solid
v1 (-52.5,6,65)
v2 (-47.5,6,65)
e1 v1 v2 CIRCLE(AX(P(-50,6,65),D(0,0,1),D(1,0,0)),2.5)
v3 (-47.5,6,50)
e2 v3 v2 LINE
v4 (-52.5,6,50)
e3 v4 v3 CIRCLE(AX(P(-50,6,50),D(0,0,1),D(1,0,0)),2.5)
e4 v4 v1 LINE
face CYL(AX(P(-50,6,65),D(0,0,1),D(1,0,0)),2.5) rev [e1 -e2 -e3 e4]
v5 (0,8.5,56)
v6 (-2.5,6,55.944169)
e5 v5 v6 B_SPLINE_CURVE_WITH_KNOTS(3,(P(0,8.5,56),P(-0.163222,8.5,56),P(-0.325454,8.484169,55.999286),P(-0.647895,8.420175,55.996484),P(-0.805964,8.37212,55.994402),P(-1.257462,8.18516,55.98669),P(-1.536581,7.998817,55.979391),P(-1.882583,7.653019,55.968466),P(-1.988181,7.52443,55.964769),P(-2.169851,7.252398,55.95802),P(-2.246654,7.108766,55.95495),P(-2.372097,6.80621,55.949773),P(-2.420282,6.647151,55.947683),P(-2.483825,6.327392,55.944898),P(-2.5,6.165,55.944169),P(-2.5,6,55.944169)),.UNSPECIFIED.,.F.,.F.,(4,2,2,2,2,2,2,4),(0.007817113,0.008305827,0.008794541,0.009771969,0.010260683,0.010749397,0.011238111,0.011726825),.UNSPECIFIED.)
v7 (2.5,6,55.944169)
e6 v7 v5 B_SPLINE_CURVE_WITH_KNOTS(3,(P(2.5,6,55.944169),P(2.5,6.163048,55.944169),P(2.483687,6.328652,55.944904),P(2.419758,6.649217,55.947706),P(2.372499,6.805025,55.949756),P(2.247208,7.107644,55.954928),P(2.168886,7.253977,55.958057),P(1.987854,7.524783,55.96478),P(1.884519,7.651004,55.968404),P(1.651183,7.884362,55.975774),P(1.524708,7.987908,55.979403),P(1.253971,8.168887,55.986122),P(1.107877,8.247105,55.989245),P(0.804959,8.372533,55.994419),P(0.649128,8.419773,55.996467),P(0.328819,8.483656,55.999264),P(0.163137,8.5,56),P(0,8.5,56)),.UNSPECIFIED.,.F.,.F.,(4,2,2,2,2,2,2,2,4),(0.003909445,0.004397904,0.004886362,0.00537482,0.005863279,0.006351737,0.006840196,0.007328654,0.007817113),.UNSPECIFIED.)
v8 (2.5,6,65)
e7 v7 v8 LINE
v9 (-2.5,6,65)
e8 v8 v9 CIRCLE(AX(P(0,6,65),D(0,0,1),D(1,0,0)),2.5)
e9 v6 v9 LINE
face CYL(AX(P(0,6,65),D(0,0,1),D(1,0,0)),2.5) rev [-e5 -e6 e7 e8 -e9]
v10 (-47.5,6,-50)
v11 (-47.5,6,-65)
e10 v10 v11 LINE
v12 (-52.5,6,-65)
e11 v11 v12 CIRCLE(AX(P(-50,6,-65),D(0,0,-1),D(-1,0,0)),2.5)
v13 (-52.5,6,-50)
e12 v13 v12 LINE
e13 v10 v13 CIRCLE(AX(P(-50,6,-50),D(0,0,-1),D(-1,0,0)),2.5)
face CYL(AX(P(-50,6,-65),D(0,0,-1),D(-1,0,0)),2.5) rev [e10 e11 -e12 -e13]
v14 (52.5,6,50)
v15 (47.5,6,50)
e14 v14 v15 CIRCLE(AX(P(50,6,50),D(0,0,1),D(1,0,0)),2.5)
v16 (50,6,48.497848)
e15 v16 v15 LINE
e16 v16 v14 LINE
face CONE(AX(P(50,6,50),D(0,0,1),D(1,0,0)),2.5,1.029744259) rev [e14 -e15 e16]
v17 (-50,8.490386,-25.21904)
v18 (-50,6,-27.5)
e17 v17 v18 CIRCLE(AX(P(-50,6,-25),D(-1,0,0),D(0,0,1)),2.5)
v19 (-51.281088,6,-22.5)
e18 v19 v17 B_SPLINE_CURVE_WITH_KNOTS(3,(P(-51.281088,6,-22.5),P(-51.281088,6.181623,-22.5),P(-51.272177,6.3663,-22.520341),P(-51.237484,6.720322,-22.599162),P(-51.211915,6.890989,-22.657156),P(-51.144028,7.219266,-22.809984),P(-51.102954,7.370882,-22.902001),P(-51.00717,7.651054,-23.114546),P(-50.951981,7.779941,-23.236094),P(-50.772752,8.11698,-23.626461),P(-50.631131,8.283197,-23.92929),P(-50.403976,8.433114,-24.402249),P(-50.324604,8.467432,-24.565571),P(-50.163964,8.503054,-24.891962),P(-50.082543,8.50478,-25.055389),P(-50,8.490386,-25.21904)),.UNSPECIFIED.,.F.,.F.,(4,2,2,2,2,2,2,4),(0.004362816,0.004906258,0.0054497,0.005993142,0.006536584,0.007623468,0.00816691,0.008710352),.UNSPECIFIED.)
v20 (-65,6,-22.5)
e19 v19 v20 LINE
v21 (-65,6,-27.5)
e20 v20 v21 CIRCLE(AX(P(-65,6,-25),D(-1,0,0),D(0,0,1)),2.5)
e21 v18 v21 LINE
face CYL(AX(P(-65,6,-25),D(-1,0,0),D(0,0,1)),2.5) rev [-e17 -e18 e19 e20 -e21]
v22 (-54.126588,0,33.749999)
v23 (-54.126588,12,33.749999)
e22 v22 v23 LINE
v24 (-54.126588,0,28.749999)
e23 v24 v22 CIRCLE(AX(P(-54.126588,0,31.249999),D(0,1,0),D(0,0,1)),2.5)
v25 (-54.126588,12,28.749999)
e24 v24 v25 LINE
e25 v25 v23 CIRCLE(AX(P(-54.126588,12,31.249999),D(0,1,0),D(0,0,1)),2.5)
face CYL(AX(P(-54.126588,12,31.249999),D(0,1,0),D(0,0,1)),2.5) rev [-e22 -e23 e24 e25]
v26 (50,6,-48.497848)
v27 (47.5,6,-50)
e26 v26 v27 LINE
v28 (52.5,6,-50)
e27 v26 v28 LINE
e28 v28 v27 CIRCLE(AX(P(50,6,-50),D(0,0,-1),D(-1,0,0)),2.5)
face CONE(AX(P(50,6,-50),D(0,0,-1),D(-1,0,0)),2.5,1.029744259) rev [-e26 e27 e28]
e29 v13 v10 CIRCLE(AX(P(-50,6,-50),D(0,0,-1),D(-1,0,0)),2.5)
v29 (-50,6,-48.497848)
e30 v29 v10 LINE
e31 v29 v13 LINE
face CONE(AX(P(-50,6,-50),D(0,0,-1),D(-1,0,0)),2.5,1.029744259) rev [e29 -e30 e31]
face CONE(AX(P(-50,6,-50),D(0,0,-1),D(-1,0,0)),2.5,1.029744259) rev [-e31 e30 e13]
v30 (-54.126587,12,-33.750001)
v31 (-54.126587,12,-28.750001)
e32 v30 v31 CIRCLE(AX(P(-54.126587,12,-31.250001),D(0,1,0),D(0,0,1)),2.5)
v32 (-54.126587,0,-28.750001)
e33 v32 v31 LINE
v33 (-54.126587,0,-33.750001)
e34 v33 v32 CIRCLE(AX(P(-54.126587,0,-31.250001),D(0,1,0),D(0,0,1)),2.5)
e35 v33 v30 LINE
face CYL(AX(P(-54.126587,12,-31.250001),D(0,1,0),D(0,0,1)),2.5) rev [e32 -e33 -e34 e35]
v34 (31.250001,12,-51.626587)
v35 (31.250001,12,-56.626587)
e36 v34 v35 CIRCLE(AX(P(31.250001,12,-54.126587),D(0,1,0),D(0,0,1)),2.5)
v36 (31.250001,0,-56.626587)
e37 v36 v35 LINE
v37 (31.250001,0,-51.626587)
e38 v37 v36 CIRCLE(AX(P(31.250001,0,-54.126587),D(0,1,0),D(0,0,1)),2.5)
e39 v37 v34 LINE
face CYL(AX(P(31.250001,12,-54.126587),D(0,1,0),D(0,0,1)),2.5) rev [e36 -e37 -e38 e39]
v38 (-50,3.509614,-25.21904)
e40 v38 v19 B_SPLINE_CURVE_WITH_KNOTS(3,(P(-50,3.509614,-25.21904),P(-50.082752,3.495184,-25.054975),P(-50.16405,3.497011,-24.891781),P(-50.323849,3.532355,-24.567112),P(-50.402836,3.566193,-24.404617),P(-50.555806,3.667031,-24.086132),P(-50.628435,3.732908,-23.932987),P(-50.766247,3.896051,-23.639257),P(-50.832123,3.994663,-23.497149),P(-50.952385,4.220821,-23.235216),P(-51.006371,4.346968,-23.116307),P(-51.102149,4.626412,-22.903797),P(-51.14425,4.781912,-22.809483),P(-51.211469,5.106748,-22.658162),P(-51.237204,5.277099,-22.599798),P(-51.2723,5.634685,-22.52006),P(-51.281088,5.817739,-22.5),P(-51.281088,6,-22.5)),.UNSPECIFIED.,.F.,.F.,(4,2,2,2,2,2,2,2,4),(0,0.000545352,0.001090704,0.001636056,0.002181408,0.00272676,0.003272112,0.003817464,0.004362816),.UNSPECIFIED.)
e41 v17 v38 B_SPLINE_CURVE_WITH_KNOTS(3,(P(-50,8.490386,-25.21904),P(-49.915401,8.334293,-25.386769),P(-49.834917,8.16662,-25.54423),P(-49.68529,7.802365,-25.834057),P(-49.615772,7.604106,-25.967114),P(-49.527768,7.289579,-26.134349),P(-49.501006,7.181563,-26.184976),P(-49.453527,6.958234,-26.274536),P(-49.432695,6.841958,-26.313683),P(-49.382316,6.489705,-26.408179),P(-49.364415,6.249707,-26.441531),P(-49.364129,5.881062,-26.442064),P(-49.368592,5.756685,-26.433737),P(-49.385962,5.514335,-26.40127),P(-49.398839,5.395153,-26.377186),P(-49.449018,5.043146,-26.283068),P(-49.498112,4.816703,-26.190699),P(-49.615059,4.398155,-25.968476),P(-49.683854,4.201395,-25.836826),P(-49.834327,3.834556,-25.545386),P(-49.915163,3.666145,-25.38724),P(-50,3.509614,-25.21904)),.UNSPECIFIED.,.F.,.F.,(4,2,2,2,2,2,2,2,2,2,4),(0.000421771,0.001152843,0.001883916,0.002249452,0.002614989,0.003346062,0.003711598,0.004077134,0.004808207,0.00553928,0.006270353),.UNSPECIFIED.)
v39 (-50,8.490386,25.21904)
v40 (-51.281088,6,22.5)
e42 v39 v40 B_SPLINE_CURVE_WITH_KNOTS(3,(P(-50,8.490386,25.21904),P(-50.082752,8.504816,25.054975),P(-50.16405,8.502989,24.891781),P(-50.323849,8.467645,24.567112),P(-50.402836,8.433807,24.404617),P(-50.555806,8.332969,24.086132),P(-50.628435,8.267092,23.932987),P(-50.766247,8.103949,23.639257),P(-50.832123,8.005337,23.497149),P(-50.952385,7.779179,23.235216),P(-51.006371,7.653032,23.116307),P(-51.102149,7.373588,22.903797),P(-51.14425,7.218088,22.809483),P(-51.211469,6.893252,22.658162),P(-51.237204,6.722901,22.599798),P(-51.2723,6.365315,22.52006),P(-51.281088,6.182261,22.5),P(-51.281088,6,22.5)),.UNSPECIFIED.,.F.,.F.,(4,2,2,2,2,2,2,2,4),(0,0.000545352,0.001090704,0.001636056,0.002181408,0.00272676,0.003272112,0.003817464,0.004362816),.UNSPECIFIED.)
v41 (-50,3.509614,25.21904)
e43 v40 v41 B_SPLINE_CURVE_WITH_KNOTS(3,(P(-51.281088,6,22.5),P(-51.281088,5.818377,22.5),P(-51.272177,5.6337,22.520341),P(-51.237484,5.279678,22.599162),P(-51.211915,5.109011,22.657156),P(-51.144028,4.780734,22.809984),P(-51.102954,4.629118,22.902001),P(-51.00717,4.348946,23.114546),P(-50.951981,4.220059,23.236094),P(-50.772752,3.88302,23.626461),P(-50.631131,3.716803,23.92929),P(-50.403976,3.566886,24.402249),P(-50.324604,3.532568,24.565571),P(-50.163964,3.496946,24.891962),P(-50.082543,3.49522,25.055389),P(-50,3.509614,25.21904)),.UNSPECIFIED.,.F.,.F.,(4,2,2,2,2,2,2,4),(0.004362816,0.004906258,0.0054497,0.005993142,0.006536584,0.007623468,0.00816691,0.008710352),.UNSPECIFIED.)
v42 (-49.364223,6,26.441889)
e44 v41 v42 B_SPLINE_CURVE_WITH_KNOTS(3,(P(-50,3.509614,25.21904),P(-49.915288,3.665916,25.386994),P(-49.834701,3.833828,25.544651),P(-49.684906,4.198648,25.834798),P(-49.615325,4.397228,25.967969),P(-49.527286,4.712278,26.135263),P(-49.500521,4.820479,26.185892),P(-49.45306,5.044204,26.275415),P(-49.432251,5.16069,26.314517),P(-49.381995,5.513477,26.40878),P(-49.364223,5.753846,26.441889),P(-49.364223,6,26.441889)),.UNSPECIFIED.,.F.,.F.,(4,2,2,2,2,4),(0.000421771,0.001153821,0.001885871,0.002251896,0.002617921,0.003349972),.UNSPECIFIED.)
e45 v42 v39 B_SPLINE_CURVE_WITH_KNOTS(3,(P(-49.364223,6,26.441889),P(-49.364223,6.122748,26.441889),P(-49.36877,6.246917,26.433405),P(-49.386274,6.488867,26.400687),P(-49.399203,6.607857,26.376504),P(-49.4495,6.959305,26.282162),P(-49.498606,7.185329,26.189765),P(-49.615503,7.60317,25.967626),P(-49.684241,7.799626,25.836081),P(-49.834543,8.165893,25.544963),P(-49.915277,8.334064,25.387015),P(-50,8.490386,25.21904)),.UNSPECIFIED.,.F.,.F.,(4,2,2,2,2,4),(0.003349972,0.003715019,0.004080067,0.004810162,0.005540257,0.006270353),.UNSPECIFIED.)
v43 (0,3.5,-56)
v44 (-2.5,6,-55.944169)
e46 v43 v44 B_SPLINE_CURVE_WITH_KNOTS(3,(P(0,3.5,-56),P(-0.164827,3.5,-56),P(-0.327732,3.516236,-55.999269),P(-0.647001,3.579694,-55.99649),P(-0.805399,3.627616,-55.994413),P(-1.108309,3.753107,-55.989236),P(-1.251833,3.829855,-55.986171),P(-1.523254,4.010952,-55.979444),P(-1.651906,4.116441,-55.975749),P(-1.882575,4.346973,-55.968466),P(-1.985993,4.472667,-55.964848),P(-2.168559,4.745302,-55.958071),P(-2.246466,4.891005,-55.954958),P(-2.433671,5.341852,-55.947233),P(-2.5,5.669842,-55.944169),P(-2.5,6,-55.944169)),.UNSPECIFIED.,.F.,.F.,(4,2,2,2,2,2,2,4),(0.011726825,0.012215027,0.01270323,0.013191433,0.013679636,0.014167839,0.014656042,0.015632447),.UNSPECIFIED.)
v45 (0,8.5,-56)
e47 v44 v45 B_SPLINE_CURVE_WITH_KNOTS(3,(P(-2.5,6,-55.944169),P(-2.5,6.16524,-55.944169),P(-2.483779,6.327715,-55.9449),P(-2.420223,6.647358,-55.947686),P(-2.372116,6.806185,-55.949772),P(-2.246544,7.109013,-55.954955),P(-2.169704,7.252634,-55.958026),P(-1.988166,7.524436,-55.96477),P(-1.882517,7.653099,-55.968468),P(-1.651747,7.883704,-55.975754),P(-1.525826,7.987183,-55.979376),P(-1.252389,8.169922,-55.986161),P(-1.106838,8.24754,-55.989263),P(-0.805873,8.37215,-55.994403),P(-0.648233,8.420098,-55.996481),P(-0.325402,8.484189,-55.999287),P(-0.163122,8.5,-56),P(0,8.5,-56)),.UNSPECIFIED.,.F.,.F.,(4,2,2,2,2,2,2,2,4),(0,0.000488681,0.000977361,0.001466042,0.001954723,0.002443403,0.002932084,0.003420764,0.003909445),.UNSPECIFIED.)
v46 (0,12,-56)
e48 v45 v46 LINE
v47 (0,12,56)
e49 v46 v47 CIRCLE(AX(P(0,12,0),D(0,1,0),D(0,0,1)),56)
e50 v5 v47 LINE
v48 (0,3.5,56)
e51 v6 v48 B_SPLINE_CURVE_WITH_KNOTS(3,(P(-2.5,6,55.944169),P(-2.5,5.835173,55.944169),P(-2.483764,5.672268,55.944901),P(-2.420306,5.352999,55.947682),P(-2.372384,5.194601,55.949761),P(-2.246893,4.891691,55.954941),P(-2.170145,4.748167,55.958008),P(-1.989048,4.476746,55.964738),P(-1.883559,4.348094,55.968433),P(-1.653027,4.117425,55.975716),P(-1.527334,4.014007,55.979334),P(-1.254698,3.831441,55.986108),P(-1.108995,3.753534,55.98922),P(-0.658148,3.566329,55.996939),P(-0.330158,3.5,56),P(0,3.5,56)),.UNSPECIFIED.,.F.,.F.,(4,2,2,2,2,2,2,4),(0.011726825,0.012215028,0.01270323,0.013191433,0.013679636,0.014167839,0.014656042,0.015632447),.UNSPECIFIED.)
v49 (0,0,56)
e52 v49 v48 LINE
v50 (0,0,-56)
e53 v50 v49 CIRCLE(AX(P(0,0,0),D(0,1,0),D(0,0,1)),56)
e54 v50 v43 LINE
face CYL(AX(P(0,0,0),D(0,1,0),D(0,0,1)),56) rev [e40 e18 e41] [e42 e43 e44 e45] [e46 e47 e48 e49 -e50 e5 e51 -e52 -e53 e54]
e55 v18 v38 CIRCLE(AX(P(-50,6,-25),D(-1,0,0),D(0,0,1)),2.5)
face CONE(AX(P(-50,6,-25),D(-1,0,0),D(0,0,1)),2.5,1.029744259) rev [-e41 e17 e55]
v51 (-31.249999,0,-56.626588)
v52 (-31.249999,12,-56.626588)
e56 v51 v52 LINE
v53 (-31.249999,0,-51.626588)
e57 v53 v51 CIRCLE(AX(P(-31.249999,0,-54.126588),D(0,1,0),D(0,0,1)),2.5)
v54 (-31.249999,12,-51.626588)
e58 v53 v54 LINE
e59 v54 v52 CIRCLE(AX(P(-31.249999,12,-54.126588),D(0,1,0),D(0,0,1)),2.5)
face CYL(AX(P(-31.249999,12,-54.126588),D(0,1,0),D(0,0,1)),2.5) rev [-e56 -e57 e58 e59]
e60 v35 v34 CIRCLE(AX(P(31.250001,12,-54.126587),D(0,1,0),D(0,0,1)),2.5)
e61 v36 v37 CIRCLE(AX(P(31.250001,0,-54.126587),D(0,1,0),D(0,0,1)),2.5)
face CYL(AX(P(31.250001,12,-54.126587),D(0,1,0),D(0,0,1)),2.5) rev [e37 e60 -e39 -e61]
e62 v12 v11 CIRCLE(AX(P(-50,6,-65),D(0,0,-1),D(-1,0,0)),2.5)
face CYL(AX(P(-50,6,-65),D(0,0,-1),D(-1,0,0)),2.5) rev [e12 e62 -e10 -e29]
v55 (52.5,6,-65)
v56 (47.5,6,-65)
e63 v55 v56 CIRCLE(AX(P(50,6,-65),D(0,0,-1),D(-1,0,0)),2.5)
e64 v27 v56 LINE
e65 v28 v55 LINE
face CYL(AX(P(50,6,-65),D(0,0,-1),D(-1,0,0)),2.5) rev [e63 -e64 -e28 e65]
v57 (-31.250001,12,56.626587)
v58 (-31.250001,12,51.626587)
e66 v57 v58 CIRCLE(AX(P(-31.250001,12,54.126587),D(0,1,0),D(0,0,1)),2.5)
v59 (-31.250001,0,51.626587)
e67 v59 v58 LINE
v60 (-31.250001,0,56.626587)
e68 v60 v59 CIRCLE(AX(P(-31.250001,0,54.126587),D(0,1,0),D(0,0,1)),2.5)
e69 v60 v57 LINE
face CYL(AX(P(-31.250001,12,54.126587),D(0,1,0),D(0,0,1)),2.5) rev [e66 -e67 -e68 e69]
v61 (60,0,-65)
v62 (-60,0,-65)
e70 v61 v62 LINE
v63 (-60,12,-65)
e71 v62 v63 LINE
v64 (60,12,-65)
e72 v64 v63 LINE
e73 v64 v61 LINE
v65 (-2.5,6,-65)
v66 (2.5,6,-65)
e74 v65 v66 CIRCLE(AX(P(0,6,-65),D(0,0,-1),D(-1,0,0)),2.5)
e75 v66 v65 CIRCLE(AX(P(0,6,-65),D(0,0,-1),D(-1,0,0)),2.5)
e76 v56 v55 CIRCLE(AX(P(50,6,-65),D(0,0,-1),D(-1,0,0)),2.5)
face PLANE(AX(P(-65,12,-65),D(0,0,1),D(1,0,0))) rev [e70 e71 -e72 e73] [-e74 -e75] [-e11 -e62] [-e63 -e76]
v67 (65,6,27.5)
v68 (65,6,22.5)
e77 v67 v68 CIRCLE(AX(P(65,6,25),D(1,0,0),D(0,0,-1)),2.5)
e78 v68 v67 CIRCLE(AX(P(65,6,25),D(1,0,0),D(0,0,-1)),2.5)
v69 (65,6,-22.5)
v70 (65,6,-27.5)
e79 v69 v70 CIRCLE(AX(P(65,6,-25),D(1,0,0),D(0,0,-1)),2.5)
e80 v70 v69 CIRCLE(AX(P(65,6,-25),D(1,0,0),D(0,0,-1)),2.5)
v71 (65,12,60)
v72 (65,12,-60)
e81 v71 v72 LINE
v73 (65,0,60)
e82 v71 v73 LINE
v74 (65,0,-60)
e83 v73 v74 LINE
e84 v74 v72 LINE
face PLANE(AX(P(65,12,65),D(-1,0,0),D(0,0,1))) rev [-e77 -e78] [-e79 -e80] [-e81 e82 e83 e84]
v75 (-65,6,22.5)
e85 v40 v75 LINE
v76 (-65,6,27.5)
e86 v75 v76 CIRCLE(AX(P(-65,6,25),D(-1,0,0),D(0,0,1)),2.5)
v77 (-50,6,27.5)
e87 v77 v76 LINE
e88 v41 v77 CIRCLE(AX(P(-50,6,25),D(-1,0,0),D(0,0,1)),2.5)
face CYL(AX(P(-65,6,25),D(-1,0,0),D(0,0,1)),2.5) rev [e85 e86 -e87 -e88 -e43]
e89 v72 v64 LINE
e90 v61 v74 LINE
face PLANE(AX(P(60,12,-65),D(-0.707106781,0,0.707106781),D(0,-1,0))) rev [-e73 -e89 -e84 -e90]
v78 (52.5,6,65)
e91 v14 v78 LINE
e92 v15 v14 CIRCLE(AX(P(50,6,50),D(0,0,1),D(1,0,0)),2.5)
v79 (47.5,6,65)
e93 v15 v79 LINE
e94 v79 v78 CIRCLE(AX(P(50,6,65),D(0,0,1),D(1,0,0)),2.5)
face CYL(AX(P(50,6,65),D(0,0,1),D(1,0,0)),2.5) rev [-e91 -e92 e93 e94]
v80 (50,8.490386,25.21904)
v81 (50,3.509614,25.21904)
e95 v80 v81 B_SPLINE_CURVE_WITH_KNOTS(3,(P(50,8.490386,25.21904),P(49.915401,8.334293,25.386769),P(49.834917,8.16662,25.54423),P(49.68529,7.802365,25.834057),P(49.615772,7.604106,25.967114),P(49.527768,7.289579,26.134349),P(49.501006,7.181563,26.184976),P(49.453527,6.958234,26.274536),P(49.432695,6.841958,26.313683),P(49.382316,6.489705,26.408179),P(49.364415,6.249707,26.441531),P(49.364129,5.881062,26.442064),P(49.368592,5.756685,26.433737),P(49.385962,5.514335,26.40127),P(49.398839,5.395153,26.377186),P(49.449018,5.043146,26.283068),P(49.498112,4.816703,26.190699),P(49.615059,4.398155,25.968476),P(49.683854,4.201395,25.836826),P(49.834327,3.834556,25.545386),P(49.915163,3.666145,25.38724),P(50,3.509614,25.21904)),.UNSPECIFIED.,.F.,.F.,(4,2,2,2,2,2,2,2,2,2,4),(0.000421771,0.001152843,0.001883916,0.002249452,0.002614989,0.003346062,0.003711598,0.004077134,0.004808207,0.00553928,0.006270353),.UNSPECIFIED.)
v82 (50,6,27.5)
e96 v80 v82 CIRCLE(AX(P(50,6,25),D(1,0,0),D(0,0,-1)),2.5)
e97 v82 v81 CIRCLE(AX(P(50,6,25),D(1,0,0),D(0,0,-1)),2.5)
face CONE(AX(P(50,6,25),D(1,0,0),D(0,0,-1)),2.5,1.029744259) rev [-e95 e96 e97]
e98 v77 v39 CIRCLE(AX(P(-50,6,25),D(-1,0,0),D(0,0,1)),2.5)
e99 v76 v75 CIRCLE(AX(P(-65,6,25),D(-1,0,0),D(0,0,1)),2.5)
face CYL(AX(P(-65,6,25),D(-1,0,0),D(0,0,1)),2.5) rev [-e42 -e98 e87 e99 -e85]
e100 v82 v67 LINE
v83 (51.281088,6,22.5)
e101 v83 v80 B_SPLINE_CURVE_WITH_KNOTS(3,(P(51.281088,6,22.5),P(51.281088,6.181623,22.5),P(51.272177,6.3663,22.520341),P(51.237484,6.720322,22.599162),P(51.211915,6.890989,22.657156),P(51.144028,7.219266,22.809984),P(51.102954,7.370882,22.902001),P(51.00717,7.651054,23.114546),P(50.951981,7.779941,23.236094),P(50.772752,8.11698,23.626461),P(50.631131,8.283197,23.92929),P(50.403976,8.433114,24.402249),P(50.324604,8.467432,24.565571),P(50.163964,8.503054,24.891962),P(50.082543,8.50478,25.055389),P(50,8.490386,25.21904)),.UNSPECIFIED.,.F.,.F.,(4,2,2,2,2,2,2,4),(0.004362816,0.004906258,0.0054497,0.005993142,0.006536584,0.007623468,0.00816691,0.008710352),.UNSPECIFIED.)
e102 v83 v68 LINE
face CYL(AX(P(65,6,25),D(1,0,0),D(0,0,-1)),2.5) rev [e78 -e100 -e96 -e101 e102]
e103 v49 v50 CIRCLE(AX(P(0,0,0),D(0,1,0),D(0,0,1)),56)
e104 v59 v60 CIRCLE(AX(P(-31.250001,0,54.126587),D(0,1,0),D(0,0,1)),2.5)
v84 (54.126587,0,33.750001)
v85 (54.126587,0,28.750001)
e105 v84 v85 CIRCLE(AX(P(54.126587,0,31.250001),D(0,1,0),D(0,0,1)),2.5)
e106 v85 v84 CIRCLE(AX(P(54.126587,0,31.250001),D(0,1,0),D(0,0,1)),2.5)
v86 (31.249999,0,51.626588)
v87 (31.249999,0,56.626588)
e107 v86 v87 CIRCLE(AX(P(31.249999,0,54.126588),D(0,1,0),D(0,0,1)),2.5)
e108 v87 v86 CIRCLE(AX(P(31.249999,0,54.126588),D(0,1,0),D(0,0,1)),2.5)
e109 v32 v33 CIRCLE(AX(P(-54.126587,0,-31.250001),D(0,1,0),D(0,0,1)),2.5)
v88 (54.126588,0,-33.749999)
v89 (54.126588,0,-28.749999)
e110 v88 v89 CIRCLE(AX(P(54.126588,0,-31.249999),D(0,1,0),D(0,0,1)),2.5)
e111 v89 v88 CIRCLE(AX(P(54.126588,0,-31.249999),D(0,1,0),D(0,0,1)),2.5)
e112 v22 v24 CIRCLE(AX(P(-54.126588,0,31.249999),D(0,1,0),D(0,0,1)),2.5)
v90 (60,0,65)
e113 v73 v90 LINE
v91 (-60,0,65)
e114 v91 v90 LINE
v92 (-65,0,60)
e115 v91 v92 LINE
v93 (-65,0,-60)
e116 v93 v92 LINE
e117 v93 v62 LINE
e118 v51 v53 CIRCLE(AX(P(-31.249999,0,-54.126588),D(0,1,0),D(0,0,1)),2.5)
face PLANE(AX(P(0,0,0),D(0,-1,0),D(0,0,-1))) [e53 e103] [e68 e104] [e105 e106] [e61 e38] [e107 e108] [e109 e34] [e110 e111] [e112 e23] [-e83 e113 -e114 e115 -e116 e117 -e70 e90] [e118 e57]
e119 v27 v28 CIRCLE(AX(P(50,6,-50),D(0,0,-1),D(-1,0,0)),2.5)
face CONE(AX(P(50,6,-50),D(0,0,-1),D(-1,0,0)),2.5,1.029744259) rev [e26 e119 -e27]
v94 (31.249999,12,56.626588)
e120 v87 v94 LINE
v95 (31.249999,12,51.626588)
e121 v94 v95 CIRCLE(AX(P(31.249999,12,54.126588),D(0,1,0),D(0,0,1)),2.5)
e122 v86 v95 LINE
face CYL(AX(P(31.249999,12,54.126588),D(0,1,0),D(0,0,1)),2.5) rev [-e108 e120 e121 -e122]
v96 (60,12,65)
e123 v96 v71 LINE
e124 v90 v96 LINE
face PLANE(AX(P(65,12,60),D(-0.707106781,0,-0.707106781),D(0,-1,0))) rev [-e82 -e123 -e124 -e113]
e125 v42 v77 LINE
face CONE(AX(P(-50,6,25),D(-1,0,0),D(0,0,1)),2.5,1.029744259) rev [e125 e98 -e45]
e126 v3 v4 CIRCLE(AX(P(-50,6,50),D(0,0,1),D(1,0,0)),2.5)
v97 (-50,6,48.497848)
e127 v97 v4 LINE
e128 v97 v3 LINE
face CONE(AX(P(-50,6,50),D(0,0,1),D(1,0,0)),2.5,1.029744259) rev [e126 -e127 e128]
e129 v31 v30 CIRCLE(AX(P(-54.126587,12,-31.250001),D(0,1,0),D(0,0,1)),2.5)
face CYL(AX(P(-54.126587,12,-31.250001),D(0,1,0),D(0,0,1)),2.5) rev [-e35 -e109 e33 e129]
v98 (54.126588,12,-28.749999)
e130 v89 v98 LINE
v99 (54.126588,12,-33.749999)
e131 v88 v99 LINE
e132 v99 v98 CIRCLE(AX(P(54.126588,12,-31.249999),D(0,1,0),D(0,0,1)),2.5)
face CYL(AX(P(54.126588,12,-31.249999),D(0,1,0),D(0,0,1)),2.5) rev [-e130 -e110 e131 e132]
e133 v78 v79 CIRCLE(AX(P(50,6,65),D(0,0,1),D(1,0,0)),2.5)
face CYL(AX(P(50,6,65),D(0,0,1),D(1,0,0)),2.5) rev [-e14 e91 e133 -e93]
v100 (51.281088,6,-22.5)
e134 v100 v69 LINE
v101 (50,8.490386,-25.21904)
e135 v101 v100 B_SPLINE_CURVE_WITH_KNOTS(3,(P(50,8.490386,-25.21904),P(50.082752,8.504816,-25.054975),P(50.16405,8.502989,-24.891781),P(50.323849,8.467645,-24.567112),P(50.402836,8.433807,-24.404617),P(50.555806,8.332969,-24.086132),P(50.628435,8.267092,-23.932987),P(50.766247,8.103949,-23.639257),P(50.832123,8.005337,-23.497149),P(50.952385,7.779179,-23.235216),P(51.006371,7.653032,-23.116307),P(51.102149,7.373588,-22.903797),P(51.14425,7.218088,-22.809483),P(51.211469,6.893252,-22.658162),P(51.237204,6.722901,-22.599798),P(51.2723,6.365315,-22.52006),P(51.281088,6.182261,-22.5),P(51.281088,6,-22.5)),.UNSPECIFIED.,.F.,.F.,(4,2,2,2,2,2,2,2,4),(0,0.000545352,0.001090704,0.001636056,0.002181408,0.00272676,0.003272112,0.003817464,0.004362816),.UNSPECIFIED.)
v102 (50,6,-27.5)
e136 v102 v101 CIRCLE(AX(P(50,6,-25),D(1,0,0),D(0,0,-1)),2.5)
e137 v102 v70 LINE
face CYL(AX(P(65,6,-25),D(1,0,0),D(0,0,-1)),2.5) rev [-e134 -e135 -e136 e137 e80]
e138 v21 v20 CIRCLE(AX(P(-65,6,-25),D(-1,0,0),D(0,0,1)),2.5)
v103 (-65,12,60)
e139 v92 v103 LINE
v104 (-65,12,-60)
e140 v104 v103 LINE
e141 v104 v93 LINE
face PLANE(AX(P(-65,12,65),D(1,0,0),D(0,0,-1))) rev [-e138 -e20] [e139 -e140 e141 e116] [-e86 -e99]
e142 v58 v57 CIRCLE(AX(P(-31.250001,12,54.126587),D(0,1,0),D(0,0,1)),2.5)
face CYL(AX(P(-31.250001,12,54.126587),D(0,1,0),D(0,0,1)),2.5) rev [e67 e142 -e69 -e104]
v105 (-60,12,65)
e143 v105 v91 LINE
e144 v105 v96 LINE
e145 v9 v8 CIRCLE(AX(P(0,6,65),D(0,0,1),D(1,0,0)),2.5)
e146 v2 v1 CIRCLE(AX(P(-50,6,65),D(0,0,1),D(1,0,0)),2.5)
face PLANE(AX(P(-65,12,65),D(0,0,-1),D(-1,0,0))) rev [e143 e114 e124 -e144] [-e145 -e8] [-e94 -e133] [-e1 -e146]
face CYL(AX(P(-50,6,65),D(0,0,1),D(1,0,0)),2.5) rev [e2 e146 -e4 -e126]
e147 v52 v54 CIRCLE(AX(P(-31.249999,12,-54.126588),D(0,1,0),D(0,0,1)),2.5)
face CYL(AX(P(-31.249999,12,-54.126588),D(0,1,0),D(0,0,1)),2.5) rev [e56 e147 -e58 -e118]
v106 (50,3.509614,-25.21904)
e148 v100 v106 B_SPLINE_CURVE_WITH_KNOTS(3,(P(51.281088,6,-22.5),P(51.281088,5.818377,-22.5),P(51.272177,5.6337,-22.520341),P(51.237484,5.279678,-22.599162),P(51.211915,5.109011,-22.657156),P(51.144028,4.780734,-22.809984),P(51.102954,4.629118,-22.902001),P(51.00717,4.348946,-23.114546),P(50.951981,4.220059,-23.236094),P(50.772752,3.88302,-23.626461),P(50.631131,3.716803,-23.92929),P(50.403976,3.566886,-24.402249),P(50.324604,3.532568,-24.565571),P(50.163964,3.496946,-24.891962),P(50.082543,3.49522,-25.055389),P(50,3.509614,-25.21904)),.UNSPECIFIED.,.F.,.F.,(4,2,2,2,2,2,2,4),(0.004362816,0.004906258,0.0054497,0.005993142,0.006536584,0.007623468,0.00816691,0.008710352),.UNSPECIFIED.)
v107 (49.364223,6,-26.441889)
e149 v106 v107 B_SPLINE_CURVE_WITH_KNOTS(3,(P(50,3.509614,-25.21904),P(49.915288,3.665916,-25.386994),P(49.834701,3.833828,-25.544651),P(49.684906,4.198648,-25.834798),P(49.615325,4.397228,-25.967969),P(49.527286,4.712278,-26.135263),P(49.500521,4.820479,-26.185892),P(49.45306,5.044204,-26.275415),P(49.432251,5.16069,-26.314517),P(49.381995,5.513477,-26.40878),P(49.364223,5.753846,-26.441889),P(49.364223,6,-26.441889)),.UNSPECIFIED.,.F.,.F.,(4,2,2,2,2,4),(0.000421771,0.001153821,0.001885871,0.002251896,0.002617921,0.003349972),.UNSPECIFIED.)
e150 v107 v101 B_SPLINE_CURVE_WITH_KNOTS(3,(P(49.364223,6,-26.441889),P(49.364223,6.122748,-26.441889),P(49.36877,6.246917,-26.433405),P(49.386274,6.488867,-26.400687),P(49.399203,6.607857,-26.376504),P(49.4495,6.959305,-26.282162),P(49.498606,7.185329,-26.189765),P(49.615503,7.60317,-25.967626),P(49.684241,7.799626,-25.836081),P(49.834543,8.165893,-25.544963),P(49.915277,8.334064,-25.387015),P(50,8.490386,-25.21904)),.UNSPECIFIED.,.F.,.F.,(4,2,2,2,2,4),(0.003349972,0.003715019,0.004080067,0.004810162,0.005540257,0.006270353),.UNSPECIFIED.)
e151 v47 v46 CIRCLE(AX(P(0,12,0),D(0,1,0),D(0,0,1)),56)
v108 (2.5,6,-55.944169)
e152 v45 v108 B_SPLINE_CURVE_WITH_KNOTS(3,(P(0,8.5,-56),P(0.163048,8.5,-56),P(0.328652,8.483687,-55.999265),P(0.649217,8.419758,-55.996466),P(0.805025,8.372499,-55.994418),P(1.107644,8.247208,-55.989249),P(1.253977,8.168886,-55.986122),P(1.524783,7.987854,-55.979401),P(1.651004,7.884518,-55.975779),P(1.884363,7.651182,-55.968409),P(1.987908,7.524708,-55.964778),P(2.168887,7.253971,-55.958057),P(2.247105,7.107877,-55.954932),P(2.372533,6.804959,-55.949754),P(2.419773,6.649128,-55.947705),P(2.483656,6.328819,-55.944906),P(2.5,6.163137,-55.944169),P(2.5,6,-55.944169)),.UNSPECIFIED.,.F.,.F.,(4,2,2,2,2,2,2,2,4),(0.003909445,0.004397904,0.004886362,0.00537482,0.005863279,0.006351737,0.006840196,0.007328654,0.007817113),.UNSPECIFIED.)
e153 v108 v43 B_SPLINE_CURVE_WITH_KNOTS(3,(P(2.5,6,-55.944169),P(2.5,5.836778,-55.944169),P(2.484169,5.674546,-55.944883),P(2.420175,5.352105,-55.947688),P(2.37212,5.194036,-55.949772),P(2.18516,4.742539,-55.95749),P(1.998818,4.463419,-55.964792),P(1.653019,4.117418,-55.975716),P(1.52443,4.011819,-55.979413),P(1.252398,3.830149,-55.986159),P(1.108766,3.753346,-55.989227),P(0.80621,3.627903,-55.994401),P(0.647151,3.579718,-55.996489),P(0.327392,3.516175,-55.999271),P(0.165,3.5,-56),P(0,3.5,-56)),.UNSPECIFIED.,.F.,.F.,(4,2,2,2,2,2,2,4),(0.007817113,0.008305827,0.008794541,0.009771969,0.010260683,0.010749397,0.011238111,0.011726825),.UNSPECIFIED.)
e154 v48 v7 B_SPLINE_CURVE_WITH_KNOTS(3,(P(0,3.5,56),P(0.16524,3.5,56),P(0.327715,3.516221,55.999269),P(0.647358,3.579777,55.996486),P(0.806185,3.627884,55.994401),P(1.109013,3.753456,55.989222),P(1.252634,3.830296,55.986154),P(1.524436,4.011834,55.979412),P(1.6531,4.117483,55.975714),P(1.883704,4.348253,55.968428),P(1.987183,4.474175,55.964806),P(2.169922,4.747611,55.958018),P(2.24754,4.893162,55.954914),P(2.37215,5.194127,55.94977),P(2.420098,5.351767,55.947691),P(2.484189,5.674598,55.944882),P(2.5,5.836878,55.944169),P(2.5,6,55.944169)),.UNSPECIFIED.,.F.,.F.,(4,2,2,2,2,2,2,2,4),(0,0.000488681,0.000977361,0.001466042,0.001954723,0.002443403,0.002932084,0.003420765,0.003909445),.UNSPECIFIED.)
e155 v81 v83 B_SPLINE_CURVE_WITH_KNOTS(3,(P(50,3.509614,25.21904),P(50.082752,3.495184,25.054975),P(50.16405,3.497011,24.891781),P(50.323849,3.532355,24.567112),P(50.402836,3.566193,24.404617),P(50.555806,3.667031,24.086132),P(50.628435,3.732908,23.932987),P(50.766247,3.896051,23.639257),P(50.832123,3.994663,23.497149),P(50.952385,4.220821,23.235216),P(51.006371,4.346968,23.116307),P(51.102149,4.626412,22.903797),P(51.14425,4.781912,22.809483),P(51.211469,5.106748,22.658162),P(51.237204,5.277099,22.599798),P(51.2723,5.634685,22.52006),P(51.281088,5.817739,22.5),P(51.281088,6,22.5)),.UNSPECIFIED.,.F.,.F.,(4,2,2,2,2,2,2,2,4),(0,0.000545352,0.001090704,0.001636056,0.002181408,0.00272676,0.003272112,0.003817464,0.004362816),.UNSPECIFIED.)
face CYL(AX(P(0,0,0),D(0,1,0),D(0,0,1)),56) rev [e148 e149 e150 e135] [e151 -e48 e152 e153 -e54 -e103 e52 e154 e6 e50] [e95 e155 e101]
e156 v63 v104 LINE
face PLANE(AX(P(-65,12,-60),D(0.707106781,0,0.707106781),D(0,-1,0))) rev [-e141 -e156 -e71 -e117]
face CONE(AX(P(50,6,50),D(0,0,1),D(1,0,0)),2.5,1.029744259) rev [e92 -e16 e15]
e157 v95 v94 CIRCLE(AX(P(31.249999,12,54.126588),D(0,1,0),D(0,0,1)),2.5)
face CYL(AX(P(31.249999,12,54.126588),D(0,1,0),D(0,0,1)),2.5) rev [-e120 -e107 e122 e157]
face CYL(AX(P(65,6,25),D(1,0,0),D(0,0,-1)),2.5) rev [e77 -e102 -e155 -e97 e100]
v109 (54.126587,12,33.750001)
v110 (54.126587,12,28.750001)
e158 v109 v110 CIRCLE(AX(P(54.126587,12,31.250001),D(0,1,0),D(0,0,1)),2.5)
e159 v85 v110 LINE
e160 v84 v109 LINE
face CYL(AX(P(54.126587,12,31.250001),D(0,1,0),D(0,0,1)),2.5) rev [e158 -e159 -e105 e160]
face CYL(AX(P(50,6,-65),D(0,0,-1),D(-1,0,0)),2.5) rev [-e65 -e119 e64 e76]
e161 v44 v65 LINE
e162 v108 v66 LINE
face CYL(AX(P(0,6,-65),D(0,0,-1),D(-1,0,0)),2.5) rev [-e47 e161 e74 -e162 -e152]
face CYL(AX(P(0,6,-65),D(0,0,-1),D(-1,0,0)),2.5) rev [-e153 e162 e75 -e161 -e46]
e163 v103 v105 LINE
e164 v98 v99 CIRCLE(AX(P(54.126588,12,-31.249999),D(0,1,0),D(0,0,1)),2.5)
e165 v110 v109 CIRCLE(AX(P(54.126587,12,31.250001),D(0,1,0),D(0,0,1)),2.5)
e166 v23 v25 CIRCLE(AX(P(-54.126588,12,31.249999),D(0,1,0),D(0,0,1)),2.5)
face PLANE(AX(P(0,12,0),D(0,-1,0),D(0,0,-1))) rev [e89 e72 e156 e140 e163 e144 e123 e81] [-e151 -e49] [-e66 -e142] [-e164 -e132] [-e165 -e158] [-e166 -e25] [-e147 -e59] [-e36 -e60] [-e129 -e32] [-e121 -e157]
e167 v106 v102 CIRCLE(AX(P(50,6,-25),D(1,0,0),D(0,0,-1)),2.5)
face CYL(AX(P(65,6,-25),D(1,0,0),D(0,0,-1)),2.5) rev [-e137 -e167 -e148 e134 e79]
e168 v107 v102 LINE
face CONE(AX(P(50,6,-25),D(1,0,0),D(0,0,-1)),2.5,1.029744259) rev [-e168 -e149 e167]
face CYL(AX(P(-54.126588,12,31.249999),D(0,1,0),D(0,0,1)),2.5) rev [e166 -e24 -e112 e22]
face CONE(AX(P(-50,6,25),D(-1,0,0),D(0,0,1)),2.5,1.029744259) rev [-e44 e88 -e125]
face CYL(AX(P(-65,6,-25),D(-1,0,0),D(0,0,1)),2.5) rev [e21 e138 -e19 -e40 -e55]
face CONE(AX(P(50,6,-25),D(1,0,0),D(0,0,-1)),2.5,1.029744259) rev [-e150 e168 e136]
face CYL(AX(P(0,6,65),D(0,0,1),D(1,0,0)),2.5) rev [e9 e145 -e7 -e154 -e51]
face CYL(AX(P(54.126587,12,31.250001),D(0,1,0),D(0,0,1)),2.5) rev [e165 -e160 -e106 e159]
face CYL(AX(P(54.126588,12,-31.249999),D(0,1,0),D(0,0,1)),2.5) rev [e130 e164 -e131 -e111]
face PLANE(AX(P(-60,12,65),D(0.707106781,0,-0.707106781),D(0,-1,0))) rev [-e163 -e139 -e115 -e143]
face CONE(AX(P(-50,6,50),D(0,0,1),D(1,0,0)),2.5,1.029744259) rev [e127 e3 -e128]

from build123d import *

# Parameters (mm, degrees)
SKETCH_1_W             = 130
SKETCH_1_H             = 130
EXTRUDE_1_DEPTH        = 12
SKETCH_2_R             = 56
CUT_EXTRUDE_1_DEPTH    = 93.703829479
HOLE_WIZARD_M6_1_D     = 5
HOLE_WIZARD_M6_2_D     = 5
HOLE_WIZARD_M6_2_DEPTH = 15
HOLE_WIZARD_M6_2_TIP   = 1.502151548
HOLE_WIZARD_M6_3_D     = 5
HOLE_WIZARD_M6_3_DEPTH = 15
HOLE_WIZARD_M6_3_TIP   = 1.502151548
HOLE_WIZARD_M6_4_D     = 5
HOLE_WIZARD_M6_4_DEPTH = 15
HOLE_WIZARD_M6_4_TIP   = 1.502151548
HOLE_WIZARD_M6_5_D     = 5
HOLE_WIZARD_M6_5_DEPTH = 15
HOLE_WIZARD_M6_5_TIP   = 1.502151548
CHAMFER_1_SIZE         = 5


with BuildPart() as part:
    # 草图1 → 凸台-拉伸1 (new body)
    with BuildSketch(Plane(origin=(0, 0, 0), x_dir=(1, 0, 0), z_dir=(0, 1, 0))):
        Rectangle(SKETCH_1_W, SKETCH_1_H)
    extrude(amount=EXTRUDE_1_DEPTH)

    # 草图2 → 切除-拉伸1 (cut, through all)
    with BuildSketch(Plane(origin=(0, 12, 0), x_dir=(1, 0, 0), z_dir=(0, 1, 0))):
        with Locations(Location((0, 0, 0), (0, 0, 270))):
            Circle(SKETCH_2_R)
    extrude(amount=-CUT_EXTRUDE_1_DEPTH, mode=Mode.SUBTRACT)

    # M6 螺纹孔1 (through all)
    with Locations(Plane(origin=(0, 12, 0), x_dir=(1, 0, 0), z_dir=(0, 1, 0))):
        with Locations((31.250000582, 54.1265874), (54.126588073, 31.249999418), (54.1265874, -31.250000582), (31.249999418, -54.126588073), (-31.250000582, -54.1265874), (-54.126588073, -31.249999418), (-54.1265874, 31.250000582), (-31.249999418, 54.126588073)):
            Hole(HOLE_WIZARD_M6_1_D / 2)

    # M6 螺纹孔2
    with Locations(Plane(origin=(65, 0, 0), x_dir=(0, 0, -1), z_dir=(1, 0, 0))):
        with Locations((-25, 6), (25, 6)):
            Hole(HOLE_WIZARD_M6_2_D / 2, depth=HOLE_WIZARD_M6_2_DEPTH)
            with Locations((0, 0, -(HOLE_WIZARD_M6_2_DEPTH + HOLE_WIZARD_M6_2_TIP / 2))):  # 118° drill point
                Cone(0, HOLE_WIZARD_M6_2_D / 2, HOLE_WIZARD_M6_2_TIP, mode=Mode.SUBTRACT)

    # M6 螺纹孔3
    with Locations(Plane.ZY.offset(65)):
        with Locations((-25, 6), (25, 6)):
            Hole(HOLE_WIZARD_M6_3_D / 2, depth=HOLE_WIZARD_M6_3_DEPTH)
            with Locations((0, 0, -(HOLE_WIZARD_M6_3_DEPTH + HOLE_WIZARD_M6_3_TIP / 2))):  # 118° drill point
                Cone(0, HOLE_WIZARD_M6_3_D / 2, HOLE_WIZARD_M6_3_TIP, mode=Mode.SUBTRACT)

    # M6 螺纹孔4
    with Locations(Plane(origin=(0, 0, -65), x_dir=(-1, 0, 0), z_dir=(0, 0, -1))):
        with Locations((-50, 6), (50, 6), (0, 6)):
            Hole(HOLE_WIZARD_M6_4_D / 2, depth=HOLE_WIZARD_M6_4_DEPTH)
            with Locations((0, 0, -(HOLE_WIZARD_M6_4_DEPTH + HOLE_WIZARD_M6_4_TIP / 2))):  # 118° drill point
                Cone(0, HOLE_WIZARD_M6_4_D / 2, HOLE_WIZARD_M6_4_TIP, mode=Mode.SUBTRACT)

    # M6 螺纹孔5
    with Locations(Plane.XY.offset(65)):
        with Locations((-50, 6), (50, 6), (0, 6)):
            Hole(HOLE_WIZARD_M6_5_D / 2, depth=HOLE_WIZARD_M6_5_DEPTH)
            with Locations((0, 0, -(HOLE_WIZARD_M6_5_DEPTH + HOLE_WIZARD_M6_5_TIP / 2))):  # 118° drill point
                Cone(0, HOLE_WIZARD_M6_5_D / 2, HOLE_WIZARD_M6_5_TIP, mode=Mode.SUBTRACT)

    # 倒角1
    chamfer_1_edges = [part.edges().sort_by_distance(p)[0] for p in [
        (65, 6, 65),
        (-65, 6, 65),
        (-65, 6, -65),
        (65, 6, -65),
    ]]
    chamfer(chamfer_1_edges, length=CHAMFER_1_SIZE)


solid = part.part
